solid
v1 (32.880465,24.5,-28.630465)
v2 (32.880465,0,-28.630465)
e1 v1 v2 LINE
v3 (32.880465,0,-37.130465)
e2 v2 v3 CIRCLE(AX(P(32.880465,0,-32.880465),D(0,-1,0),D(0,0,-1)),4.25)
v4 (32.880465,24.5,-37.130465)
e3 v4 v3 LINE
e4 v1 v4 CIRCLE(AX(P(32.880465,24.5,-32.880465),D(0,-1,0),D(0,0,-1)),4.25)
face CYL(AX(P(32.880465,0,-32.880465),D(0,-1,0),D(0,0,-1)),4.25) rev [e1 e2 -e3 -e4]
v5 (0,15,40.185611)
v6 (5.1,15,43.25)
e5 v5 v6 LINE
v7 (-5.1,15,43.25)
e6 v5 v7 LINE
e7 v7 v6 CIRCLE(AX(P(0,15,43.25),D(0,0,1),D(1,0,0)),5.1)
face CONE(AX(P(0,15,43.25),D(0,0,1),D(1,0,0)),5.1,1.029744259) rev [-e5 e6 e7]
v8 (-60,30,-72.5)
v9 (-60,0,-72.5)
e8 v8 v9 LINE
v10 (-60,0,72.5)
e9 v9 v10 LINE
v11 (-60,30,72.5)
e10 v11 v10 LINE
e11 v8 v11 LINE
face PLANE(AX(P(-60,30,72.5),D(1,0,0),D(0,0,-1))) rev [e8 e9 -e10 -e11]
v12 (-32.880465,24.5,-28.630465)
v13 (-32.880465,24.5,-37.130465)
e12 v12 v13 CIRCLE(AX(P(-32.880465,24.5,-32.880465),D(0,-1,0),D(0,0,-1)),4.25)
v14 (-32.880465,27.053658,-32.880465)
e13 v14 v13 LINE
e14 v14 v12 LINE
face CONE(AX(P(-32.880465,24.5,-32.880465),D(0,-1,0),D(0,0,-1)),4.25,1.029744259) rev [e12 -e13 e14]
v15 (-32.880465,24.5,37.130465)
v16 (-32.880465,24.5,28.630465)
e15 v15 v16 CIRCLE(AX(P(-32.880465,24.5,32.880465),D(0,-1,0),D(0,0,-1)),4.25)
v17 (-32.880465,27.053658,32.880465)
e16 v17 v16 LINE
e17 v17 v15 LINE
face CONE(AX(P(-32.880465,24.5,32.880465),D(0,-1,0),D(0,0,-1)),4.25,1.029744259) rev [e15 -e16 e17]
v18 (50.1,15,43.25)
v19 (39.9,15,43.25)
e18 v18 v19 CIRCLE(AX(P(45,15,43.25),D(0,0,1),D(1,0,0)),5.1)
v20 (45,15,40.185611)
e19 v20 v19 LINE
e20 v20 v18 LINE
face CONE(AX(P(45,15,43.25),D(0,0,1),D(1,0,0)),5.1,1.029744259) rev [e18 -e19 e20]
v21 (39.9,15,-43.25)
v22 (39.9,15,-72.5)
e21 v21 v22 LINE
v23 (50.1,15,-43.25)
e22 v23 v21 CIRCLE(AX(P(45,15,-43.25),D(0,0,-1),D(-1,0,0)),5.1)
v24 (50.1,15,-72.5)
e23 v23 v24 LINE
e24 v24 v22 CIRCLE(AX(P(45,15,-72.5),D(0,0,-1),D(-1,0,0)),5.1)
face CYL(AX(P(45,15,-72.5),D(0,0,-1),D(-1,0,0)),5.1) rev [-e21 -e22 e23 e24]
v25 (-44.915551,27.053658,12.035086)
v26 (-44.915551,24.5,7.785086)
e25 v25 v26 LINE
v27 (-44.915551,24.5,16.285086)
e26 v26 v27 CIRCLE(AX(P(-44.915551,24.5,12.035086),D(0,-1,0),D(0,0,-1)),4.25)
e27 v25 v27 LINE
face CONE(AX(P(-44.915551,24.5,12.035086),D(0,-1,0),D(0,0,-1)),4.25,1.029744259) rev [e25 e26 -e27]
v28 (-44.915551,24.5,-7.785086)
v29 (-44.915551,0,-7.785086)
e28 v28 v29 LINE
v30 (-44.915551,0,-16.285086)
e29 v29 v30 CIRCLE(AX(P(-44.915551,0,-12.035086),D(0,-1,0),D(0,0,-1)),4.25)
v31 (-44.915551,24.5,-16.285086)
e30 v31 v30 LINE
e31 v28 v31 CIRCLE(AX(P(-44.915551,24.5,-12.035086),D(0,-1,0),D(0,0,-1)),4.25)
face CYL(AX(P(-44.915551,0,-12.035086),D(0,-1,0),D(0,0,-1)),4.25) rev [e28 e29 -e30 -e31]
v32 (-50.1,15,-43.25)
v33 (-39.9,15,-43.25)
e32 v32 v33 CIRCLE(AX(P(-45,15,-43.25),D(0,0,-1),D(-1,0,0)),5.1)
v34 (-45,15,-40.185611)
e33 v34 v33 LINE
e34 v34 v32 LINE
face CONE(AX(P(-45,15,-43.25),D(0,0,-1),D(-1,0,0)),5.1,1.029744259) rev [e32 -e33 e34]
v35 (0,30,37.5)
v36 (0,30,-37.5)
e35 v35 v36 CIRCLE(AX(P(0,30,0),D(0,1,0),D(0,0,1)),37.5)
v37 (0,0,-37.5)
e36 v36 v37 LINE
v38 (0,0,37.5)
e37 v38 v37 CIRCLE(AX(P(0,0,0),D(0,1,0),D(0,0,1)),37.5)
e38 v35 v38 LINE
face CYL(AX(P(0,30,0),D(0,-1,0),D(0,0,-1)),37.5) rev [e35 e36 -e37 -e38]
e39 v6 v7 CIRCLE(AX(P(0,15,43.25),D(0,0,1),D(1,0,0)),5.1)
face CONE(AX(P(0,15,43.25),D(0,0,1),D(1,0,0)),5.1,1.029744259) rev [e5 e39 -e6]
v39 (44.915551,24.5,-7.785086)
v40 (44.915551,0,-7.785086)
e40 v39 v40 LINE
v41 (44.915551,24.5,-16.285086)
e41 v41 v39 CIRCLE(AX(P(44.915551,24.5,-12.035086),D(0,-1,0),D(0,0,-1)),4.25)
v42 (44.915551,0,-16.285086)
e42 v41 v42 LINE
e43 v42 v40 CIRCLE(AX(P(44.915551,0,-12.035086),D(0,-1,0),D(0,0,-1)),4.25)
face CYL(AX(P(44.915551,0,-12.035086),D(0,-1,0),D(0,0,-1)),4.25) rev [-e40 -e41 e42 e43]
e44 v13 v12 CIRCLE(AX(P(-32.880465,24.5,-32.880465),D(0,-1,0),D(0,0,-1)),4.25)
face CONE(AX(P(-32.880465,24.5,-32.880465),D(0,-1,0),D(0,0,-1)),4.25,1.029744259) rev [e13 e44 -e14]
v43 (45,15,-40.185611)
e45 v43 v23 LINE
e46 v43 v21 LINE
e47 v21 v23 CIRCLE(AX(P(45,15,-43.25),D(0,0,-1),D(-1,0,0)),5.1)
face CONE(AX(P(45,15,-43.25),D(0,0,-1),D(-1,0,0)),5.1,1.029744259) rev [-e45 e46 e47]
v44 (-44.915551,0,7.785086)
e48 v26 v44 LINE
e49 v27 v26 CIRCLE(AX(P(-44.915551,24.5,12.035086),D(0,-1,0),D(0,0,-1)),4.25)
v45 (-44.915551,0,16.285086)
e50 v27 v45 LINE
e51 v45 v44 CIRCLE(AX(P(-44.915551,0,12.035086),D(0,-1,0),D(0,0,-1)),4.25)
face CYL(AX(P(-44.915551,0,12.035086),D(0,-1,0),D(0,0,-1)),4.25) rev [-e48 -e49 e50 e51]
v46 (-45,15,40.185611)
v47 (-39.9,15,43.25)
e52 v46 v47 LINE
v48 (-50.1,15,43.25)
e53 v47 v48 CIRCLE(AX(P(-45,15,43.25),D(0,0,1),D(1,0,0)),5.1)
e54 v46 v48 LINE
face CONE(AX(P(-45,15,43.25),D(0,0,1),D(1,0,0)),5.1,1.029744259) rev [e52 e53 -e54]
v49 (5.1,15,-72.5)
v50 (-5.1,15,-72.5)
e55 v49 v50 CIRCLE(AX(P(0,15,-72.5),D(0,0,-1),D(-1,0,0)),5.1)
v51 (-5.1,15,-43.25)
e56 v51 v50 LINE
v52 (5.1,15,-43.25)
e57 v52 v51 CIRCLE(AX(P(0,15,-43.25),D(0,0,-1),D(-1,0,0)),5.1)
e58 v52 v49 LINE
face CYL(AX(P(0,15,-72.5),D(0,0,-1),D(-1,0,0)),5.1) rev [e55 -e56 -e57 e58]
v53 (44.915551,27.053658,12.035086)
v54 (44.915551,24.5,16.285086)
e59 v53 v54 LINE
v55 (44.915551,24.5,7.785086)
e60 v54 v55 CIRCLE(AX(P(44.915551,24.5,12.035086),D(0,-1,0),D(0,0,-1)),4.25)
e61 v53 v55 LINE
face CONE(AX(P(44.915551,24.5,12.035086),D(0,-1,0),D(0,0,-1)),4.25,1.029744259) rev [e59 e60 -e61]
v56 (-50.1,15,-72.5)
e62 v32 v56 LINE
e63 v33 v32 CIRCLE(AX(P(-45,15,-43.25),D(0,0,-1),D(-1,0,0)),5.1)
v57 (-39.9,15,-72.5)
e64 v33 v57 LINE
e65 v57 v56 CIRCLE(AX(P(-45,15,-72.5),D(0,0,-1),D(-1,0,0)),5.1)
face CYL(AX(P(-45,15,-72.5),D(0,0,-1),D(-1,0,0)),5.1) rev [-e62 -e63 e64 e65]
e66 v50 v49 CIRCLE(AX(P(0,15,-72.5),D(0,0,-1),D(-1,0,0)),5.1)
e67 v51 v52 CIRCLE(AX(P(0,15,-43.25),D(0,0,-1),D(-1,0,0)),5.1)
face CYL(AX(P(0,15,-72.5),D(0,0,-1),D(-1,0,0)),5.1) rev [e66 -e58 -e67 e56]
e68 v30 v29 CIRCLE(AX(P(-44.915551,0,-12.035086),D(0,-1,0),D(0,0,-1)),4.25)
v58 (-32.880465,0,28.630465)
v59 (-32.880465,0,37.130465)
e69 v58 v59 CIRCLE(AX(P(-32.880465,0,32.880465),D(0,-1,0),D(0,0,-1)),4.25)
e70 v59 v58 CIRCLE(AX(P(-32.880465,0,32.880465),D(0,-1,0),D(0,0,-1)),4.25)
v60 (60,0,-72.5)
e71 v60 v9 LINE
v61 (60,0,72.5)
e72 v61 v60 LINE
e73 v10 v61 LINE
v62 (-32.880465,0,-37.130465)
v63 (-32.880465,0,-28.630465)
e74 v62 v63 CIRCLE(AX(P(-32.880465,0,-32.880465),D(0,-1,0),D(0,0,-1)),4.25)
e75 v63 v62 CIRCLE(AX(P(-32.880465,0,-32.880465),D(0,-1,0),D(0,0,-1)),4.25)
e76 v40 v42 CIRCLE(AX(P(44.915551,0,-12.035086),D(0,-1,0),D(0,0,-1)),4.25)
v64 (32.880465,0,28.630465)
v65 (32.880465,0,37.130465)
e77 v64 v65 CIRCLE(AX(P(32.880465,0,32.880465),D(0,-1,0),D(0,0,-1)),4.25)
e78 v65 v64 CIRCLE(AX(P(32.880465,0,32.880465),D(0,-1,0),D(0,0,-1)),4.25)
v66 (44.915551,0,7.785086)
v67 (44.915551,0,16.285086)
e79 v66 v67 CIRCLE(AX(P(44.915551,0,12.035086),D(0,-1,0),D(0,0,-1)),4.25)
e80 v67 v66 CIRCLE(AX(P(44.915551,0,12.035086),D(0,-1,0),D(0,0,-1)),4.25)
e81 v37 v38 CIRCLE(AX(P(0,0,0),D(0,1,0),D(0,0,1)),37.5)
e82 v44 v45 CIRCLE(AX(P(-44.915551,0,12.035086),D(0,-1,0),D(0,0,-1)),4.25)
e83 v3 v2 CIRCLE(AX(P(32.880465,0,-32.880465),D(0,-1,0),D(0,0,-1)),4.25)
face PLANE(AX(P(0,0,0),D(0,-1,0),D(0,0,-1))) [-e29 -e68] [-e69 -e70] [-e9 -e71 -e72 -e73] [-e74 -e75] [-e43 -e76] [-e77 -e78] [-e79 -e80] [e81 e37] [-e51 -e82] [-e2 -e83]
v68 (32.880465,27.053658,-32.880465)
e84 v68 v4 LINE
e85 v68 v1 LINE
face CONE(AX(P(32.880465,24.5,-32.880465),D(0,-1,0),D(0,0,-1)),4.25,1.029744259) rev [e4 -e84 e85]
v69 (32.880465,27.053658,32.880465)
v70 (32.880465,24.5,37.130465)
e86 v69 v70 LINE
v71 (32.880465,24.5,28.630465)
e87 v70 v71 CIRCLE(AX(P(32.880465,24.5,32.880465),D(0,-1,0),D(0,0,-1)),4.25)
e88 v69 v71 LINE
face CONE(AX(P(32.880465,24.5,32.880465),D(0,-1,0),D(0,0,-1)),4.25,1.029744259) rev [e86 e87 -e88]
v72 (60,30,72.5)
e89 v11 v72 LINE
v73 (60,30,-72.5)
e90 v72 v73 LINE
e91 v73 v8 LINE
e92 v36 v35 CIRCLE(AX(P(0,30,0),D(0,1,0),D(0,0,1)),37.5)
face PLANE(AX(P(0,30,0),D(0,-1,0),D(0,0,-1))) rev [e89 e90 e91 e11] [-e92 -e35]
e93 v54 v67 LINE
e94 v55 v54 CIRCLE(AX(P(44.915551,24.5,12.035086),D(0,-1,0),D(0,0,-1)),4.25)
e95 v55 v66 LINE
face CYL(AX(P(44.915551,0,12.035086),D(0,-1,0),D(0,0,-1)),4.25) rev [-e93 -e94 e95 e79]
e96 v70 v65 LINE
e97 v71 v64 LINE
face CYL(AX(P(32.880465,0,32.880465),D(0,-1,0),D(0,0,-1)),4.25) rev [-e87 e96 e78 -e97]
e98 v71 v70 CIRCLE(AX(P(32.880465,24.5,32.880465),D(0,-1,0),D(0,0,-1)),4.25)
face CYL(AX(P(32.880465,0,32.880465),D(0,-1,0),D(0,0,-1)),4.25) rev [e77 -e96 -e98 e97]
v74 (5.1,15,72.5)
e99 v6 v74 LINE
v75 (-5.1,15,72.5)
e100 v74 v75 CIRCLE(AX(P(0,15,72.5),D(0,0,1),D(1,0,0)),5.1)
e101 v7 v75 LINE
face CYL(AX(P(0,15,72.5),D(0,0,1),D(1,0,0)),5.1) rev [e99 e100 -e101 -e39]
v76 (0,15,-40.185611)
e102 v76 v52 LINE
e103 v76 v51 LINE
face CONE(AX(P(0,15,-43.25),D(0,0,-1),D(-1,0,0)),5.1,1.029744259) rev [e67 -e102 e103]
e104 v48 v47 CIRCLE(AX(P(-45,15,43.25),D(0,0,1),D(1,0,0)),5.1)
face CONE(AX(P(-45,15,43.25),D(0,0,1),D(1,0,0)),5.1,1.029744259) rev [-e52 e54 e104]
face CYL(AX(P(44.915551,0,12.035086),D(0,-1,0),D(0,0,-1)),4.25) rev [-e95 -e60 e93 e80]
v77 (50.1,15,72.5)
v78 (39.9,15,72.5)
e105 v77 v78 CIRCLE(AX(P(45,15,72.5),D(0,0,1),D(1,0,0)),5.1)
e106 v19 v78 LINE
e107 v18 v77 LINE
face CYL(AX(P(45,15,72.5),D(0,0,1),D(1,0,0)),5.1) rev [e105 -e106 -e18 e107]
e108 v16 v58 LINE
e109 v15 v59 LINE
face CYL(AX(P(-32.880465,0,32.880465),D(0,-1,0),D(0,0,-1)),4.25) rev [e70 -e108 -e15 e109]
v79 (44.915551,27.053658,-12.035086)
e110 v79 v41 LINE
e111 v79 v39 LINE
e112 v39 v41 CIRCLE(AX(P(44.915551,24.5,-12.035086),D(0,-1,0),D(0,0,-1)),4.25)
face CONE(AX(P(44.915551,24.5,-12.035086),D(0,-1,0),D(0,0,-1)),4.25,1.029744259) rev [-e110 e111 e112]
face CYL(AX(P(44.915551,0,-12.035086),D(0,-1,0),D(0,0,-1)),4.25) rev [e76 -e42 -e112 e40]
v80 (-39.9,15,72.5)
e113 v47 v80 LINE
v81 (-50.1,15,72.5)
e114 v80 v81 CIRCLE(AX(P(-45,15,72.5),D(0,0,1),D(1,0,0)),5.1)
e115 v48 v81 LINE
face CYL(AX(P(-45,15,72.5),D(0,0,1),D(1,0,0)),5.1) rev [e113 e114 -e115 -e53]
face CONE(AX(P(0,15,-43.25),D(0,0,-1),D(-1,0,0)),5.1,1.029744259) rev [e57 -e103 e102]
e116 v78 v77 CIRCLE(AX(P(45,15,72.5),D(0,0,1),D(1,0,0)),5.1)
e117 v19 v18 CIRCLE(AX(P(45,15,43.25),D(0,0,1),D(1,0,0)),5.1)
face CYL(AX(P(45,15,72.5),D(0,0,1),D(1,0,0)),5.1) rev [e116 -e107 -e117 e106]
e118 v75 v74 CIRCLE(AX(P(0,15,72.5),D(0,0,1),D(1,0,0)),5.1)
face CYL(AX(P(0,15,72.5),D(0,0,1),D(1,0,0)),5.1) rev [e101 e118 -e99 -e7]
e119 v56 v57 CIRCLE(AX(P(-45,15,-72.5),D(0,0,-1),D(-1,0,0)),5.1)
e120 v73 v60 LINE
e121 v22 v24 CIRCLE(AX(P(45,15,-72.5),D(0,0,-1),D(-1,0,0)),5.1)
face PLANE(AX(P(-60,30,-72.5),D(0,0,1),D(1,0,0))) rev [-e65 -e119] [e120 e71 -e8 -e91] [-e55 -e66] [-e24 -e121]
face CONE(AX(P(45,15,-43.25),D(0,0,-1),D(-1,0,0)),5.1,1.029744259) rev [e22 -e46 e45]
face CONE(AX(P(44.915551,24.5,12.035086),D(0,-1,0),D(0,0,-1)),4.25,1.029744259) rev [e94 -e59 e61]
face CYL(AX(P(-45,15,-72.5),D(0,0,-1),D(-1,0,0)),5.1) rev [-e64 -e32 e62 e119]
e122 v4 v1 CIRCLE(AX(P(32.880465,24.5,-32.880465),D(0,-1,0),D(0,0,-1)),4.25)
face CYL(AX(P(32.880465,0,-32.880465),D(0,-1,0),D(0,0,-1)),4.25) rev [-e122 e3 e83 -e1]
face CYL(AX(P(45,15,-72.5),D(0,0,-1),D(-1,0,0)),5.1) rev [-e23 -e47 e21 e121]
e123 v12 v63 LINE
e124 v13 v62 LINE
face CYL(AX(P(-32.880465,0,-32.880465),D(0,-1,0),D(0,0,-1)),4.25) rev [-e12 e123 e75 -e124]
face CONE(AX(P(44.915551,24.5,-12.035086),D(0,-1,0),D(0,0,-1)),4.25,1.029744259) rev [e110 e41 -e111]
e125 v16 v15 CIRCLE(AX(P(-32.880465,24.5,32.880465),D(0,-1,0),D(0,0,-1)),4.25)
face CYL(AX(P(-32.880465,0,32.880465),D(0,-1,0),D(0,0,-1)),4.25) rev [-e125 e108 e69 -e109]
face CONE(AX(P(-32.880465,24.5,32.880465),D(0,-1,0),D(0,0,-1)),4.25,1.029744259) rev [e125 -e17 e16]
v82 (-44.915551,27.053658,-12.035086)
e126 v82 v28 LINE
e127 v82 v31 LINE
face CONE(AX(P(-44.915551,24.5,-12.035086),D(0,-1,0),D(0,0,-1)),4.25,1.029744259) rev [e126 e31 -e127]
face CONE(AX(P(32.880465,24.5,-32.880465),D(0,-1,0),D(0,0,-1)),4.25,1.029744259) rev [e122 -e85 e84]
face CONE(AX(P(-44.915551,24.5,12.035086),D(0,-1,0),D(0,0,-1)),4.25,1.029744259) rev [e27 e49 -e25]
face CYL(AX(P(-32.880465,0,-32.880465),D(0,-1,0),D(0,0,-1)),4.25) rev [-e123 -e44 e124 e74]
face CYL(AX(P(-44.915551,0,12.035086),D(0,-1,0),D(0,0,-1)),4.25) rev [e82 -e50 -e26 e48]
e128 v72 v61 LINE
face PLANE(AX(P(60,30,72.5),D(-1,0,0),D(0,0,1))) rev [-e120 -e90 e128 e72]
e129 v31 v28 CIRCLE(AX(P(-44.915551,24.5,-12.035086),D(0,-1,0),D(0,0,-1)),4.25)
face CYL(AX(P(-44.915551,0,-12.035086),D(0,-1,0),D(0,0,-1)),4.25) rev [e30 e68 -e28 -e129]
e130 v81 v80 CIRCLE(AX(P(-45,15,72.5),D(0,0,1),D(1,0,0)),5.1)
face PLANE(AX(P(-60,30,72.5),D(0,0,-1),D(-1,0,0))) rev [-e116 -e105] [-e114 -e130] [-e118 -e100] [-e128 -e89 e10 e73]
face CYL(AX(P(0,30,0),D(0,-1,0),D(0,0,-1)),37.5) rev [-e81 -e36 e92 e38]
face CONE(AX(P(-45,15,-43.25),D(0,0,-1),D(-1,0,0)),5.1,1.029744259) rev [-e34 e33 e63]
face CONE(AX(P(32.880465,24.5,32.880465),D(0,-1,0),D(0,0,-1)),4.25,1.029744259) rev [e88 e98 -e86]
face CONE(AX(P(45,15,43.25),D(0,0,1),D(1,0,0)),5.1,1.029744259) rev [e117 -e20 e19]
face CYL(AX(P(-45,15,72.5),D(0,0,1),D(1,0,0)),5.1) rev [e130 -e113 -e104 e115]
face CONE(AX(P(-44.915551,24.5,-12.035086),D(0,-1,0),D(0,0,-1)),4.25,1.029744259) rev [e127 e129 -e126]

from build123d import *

# Parameters (mm, degrees)
SKETCH_1_W                   = 120
SKETCH_1_H                   = 145
SKETCH_1_R                   = 37.5
EXTRUDE_1_DEPTH              = 30
HOLE_WIZARD_M10_1_D          = 8.5
HOLE_WIZARD_M10_1_DEPTH      = 24.5
HOLE_WIZARD_M10_1_TIP        = 2.553657631
HOLE_WIZARD_M12_1_AT_2_COUNT = 2
HOLE_WIZARD_M12_1_AT_2_PITCH = 45
HOLE_WIZARD_M12_1_AT_3_COUNT = 2
HOLE_WIZARD_M12_1_AT_3_PITCH = 90


with BuildPart() as part:
    # 草图1 → 凸台-拉伸1 (new body)
    with BuildSketch(Plane(origin=(0, 0, 0), x_dir=(1, 0, 0), z_dir=(0, 1, 0))):
        Rectangle(SKETCH_1_W, SKETCH_1_H)
        with Locations(Location((0, 0, 0), (0, 0, 270))):
            Circle(SKETCH_1_R, mode=Mode.SUBTRACT)
    extrude(amount=EXTRUDE_1_DEPTH)

    # M10 螺纹孔1
    with Locations(Plane(origin=(0, 0, 0), x_dir=(-1, 0, 0), z_dir=(0, -1, 0))):
        with Locations((-32.880465325, -32.880465325), (-44.915550922, -12.035085597), (-44.915550922, 12.035085597), (-32.880465325, 32.880465325), (32.880465325, 32.880465325), (44.915550922, 12.035085597), (44.915550922, -12.035085597), (32.880465325, -32.880465325)):
            Hole(HOLE_WIZARD_M10_1_D / 2, depth=HOLE_WIZARD_M10_1_DEPTH)
            with Locations((0, 0, -(HOLE_WIZARD_M10_1_DEPTH + HOLE_WIZARD_M10_1_TIP / 2))):  # 118° drill point
                Cone(0, HOLE_WIZARD_M10_1_D / 2, HOLE_WIZARD_M10_1_TIP, mode=Mode.SUBTRACT)

    # 草图5 → M12 螺纹孔1 (revolve, cut)
    with BuildSketch(Plane(origin=(-45, 15, -72.5), x_dir=(0, 1, 0), z_dir=(1, 0, 0))):
        Polygon((0, 0), (0, 32.314389157), (5.1, 29.25), (5.1, 0), align=None)
    hole_wizard_m12_1 = revolve(axis=Axis((-45, 15, -78.85), (0, 0, 1)), mode=Mode.SUBTRACT)

    # M12 螺纹孔1 at 2: M12 螺纹孔1 ×2
    with Locations(*[(i * HOLE_WIZARD_M12_1_AT_2_PITCH, 0, 0) for i in range(1, HOLE_WIZARD_M12_1_AT_2_COUNT)]):
        add(hole_wizard_m12_1, mode=Mode.SUBTRACT)

    # M12 螺纹孔1 at 3: M12 螺纹孔1 ×2
    with Locations(*[(i * HOLE_WIZARD_M12_1_AT_3_PITCH, 0, 0) for i in range(1, HOLE_WIZARD_M12_1_AT_3_COUNT)]):
        add(hole_wizard_m12_1, mode=Mode.SUBTRACT)

    # 镜向1: M12 螺纹孔1 across plane
    add(hole_wizard_m12_1.mirror(Plane.XY), mode=Mode.SUBTRACT)

    # 镜向1 copy 1 sketch → 镜向1 copy 1 (revolve, cut)
    with BuildSketch(Plane(origin=(0, 15, 72.5), x_dir=(0, 1, 0), z_dir=(1, 0, 0))):
        Polygon((0, 0), (0, -32.314389157), (5.1, -29.25), (5.1, 0), align=None)
    revolve(axis=Axis((0, 15, 78.85), (0, 0, 1)), mode=Mode.SUBTRACT)

    # 镜向1 copy 2 sketch → 镜向1 copy 2 (revolve, cut)
    with BuildSketch(Plane(origin=(45, 15, 72.5), x_dir=(0, 1, 0), z_dir=(1, 0, 0))):
        Polygon((0, 0), (0, -32.314389157), (5.1, -29.25), (5.1, 0), align=None)
    revolve(axis=Axis((45, 15, 78.85), (0, 0, 1)), mode=Mode.SUBTRACT)


solid = part.part
